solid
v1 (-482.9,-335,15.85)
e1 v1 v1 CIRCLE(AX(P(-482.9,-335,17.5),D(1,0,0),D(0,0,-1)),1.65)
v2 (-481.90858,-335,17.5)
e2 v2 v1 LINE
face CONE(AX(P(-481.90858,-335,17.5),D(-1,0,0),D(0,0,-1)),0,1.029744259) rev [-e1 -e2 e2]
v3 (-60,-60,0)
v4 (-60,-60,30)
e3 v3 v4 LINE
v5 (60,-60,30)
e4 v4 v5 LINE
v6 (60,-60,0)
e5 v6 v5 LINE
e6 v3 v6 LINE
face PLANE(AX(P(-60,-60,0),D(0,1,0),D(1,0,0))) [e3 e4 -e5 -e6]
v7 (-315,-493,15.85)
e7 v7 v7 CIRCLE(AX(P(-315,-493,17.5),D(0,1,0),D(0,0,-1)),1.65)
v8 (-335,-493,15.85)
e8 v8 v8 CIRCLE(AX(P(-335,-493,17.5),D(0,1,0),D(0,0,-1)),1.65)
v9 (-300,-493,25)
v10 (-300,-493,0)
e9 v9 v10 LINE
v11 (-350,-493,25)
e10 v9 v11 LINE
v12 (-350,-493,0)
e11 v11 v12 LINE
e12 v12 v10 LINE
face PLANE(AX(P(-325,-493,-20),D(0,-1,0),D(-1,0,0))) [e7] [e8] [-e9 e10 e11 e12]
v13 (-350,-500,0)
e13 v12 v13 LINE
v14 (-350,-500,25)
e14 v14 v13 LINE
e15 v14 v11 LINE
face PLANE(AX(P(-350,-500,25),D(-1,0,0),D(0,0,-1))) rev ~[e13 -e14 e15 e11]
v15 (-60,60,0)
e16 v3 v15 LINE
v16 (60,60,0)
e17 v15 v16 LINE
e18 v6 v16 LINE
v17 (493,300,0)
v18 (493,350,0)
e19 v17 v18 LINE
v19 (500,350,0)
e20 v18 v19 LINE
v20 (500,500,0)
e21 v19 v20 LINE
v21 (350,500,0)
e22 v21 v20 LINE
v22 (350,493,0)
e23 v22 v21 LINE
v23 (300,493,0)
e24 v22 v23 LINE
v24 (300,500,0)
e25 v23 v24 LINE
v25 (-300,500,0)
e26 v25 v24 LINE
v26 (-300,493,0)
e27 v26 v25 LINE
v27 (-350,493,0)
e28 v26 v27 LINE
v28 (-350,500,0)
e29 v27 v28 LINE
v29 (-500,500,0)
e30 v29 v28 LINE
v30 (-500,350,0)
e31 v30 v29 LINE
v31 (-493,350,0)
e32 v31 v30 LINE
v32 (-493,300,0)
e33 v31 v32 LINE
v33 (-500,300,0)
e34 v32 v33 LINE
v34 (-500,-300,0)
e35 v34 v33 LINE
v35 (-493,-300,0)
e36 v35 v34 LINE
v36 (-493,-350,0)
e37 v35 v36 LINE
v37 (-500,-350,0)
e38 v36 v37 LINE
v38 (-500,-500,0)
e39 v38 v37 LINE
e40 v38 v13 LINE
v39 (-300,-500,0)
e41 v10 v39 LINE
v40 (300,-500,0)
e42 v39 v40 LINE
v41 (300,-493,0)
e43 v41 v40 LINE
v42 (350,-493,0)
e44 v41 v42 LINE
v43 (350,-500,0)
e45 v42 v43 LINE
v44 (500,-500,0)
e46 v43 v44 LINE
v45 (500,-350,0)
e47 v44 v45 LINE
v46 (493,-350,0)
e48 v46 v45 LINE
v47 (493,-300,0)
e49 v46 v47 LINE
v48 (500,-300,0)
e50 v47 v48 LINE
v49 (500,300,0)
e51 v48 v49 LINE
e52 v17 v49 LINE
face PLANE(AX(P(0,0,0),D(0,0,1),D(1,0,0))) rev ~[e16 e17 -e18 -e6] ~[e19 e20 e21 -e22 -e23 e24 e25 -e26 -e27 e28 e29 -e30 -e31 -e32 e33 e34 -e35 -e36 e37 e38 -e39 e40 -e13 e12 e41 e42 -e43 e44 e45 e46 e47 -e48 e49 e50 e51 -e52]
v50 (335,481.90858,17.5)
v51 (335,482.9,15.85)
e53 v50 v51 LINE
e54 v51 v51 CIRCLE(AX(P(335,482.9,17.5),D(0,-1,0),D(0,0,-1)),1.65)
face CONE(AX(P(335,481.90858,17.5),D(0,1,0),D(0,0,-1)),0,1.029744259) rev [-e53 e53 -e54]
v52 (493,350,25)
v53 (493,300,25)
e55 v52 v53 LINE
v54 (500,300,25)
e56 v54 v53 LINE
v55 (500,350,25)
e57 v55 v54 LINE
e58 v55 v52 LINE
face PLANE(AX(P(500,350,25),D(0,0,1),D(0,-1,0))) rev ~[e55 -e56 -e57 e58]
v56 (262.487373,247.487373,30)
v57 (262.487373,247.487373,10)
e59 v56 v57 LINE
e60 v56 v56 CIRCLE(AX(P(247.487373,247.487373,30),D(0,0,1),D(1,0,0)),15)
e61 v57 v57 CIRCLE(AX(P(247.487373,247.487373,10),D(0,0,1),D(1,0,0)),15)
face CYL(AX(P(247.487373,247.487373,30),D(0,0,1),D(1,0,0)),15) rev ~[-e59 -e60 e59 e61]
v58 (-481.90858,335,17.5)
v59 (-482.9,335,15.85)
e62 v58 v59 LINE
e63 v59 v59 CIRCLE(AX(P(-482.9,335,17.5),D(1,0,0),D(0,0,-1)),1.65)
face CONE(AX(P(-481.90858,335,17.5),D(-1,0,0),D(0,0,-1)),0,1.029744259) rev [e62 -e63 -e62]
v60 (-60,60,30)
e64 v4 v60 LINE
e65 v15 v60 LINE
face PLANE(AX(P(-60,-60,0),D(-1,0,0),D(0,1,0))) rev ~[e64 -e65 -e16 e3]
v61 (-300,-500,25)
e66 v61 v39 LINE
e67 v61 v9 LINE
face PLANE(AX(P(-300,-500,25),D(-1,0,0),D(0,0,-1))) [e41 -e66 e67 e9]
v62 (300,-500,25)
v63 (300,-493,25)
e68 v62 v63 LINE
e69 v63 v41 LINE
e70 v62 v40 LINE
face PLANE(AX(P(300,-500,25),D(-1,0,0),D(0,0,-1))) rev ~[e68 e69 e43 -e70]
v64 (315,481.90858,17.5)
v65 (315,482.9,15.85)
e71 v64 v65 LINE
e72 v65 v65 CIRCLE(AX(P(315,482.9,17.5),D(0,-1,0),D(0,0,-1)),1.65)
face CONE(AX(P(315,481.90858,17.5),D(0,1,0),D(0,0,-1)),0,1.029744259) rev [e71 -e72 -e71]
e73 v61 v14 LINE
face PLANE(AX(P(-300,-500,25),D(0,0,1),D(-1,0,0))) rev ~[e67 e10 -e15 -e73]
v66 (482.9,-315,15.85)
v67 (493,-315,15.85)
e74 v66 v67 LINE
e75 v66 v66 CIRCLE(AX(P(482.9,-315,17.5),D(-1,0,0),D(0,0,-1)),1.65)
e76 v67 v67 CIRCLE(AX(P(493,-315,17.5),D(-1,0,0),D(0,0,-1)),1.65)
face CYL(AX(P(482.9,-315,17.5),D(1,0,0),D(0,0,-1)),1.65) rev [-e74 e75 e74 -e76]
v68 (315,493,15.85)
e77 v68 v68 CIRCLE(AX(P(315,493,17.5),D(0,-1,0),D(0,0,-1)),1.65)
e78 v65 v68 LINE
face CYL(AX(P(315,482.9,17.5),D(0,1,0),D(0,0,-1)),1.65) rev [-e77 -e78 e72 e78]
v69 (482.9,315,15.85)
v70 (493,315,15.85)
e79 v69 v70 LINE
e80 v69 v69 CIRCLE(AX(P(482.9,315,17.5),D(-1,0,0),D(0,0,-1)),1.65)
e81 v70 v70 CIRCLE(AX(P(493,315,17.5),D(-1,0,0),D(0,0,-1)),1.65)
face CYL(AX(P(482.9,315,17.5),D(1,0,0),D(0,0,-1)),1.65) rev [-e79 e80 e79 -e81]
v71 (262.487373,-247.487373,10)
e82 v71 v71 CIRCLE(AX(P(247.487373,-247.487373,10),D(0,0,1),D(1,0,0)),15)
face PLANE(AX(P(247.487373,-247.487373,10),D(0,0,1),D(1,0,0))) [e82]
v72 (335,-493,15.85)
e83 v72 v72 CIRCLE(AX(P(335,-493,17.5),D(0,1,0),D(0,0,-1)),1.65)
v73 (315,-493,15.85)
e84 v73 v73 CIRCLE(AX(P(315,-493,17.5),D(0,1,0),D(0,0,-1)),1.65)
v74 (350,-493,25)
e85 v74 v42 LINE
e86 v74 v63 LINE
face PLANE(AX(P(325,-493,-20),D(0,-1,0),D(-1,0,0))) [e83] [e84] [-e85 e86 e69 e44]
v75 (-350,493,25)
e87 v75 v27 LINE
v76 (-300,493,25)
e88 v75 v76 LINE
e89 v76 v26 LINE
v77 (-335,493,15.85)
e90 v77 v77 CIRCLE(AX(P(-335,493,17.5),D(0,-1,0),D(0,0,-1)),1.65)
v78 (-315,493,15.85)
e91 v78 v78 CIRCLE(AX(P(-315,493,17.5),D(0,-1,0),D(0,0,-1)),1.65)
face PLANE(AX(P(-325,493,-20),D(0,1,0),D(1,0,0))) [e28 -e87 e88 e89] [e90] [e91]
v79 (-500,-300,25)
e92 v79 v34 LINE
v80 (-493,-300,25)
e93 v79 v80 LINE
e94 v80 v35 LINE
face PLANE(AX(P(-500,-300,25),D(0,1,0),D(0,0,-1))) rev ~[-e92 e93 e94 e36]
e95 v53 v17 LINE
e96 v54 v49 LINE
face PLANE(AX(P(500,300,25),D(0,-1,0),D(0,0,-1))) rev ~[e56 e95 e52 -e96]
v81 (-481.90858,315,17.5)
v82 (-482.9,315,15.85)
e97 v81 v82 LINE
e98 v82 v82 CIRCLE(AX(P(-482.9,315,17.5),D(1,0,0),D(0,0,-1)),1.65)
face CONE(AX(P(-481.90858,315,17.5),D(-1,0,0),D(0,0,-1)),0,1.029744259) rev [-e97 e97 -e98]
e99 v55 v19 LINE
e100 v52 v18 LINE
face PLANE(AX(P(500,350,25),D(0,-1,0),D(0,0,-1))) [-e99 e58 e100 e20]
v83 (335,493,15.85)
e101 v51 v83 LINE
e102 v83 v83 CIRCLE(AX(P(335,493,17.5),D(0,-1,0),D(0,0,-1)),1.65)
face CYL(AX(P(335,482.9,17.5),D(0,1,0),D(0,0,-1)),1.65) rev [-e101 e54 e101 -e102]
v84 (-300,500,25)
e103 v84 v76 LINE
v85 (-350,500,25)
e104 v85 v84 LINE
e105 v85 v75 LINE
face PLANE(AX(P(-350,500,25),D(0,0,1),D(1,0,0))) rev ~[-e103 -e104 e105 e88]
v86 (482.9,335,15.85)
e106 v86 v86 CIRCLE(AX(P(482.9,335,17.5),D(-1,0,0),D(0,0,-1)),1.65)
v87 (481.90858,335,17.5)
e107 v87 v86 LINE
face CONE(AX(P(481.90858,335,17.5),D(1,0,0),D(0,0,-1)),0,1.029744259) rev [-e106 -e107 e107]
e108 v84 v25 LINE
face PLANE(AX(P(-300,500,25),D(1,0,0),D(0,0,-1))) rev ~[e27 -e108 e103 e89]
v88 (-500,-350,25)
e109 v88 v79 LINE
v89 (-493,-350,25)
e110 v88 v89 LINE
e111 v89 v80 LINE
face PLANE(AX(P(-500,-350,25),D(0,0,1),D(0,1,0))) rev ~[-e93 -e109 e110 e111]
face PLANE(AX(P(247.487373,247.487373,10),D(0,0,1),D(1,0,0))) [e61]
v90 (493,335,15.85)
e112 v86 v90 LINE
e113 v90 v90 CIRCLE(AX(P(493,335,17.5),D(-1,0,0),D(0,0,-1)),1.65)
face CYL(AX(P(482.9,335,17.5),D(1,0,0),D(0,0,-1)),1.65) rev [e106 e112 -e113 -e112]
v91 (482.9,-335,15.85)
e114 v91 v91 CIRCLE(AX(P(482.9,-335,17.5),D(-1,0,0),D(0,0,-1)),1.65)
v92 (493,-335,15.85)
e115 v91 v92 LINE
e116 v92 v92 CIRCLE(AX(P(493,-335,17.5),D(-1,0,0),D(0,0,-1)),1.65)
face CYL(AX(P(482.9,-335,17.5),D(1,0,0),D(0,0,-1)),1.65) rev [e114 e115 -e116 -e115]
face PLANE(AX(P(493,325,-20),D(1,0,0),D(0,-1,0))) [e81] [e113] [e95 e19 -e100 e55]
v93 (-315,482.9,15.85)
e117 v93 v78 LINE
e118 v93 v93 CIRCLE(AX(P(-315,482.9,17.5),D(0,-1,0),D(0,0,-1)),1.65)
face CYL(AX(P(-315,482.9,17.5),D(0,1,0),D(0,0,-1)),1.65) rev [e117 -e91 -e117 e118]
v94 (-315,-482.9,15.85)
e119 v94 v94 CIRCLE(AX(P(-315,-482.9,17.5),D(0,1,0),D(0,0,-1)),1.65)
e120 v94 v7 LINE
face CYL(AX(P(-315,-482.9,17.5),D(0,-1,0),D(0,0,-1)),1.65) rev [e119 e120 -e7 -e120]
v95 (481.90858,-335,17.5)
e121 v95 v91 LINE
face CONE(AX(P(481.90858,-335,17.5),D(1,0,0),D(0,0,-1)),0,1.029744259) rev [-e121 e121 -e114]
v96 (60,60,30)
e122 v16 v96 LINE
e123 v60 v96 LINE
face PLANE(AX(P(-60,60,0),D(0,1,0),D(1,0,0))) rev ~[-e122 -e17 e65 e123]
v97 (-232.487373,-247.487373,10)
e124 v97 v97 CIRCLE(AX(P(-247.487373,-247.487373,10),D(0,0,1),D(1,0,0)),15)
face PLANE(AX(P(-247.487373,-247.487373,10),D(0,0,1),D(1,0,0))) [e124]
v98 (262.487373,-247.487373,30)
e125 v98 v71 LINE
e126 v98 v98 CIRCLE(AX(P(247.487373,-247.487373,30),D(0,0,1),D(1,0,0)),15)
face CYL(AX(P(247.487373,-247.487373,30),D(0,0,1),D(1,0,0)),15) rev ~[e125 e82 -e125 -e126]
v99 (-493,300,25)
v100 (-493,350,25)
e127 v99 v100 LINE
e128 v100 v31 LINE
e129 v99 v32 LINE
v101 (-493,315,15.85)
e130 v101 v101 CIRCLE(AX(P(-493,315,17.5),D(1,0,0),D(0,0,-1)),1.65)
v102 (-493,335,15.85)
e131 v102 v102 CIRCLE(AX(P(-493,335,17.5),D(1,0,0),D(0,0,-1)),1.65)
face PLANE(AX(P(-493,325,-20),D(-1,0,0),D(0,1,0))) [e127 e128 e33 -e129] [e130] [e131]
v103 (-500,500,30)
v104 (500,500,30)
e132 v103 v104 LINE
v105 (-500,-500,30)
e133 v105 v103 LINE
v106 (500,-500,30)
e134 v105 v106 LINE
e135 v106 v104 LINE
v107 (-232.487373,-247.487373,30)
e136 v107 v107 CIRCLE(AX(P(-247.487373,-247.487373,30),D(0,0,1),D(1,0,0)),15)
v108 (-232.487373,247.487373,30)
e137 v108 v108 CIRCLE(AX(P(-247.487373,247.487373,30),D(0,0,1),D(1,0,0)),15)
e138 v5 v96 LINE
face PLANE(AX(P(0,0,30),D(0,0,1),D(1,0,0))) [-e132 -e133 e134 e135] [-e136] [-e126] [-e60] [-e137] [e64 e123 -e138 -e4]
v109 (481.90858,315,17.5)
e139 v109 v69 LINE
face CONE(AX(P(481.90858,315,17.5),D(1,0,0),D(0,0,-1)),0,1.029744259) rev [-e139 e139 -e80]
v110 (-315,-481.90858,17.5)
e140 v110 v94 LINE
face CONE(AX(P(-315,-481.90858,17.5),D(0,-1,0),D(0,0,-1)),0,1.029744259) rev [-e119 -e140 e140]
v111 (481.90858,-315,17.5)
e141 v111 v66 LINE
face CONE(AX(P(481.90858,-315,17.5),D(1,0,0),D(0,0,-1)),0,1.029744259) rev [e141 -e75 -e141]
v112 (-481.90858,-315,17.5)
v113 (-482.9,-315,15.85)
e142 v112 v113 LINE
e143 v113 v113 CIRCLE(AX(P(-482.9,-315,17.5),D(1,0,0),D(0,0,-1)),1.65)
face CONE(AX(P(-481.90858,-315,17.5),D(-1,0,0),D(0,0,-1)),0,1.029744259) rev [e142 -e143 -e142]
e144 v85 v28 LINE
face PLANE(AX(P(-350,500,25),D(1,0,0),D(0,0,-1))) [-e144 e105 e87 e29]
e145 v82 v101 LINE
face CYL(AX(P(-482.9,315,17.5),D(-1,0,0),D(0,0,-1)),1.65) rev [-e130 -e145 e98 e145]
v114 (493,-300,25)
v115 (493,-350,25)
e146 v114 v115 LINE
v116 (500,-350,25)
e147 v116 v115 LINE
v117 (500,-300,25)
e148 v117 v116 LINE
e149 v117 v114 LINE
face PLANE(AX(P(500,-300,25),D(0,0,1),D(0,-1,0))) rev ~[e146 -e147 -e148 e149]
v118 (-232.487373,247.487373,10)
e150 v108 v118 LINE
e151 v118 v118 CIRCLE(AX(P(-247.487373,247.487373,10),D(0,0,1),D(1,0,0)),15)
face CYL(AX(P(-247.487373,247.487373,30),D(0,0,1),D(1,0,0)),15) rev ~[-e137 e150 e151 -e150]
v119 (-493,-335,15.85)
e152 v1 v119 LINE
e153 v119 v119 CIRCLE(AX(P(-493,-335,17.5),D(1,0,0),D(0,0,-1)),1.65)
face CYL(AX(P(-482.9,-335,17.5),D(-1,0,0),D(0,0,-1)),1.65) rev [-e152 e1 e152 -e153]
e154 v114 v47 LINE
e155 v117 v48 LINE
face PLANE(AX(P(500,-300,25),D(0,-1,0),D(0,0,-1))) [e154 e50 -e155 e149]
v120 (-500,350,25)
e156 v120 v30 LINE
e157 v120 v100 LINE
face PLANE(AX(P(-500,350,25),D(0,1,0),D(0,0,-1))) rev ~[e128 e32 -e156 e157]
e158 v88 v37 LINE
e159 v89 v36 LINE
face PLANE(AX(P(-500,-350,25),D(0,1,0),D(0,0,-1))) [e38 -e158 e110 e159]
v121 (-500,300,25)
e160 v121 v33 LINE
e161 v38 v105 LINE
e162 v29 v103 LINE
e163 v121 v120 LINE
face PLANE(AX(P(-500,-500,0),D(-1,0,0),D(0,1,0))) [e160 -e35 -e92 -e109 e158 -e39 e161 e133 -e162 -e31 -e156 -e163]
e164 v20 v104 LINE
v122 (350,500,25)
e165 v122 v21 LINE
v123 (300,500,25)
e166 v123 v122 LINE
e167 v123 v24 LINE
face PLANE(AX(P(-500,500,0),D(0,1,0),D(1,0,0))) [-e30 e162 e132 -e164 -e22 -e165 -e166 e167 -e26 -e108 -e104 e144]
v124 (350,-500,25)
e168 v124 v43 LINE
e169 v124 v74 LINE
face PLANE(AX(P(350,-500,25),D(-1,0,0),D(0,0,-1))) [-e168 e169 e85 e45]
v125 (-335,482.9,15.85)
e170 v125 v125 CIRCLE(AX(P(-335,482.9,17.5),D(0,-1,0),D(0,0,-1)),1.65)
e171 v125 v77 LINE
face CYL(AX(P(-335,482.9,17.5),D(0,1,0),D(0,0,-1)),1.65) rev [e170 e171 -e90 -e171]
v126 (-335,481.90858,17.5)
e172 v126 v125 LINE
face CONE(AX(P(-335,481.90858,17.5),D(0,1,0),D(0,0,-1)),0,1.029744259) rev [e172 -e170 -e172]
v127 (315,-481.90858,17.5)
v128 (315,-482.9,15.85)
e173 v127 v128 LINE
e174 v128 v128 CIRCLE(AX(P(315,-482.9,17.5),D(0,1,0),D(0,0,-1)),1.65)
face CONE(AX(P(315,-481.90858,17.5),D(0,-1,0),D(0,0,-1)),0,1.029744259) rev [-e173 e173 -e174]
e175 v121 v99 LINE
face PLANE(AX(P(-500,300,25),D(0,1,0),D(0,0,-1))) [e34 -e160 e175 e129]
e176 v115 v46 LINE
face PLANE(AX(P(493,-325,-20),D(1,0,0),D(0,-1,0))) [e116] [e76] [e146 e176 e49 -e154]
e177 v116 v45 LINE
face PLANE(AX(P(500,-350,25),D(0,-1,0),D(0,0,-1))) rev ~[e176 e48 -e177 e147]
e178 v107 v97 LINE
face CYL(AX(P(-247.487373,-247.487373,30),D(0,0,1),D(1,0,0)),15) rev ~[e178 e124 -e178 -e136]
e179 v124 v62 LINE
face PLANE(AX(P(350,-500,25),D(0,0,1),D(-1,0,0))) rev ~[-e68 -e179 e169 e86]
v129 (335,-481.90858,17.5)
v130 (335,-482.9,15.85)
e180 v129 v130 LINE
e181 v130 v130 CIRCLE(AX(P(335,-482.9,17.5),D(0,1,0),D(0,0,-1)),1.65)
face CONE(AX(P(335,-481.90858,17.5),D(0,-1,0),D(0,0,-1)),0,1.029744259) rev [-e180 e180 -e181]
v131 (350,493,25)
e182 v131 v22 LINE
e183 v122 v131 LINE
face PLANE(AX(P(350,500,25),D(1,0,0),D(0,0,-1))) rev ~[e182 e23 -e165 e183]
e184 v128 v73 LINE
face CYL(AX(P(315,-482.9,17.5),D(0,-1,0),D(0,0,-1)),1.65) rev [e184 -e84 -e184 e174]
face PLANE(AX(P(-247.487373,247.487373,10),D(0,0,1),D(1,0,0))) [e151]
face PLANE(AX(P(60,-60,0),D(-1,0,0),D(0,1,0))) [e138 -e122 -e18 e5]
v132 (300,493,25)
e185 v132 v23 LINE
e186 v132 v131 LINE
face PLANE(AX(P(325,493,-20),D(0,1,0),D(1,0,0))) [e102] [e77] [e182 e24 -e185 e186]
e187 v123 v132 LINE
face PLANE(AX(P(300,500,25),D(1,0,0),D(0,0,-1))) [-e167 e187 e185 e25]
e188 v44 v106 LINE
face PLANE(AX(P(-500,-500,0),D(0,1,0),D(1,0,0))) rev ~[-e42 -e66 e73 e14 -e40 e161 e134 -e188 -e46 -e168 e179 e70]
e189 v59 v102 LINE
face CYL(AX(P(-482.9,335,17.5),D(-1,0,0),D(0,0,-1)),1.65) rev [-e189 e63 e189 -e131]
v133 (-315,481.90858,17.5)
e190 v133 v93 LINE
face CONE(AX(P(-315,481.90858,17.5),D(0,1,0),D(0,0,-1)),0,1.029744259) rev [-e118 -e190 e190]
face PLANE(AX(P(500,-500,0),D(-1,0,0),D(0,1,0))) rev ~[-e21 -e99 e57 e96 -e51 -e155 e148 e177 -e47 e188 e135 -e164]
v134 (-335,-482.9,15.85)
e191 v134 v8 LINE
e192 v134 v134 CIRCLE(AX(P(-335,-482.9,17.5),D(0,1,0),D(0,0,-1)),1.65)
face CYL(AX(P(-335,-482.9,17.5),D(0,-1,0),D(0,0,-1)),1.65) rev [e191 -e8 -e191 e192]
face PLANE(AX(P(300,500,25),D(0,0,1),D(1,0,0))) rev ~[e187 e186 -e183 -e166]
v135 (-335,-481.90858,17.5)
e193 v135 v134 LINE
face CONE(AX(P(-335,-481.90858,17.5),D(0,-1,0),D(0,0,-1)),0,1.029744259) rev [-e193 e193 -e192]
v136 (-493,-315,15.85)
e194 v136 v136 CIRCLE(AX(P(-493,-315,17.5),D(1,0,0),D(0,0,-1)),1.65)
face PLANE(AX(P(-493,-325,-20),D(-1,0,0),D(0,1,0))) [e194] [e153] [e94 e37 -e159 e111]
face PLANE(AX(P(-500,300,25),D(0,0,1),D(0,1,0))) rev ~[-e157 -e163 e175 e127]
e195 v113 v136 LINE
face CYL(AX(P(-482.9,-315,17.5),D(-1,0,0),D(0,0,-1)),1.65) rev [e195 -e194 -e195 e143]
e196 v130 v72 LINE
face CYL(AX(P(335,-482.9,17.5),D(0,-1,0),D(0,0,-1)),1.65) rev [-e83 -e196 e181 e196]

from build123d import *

# Parameters (mm, degrees)
SKETCH1_W                  = 1000
SKETCH1_H                  = 1000
SKETCH1_W_2                = 120
SKETCH1_H_2                = 120
BOSS_EXTRUDE1_DEPTH        = 30
SKETCH2_R                  = 15
CUT_EXTRUDE1_DEPTH         = 20
SKETCH3_W                  = 50
SKETCH3_H                  = 90
CUT_EXTRUDE2_DEPTH         = 7
CIRPATTERN1_COUNT          = 4
M4_TAPPED_HOLE1_AT_2_COUNT = 2
M4_TAPPED_HOLE1_AT_2_PITCH = 20
M4_TAPPED_HOLE1_AT_3_COUNT = 2
M4_TAPPED_HOLE1_AT_3_PITCH = 650
M4_TAPPED_HOLE1_AT_4_COUNT = 2
M4_TAPPED_HOLE1_AT_4_PITCH = 670
CIRPATTERN2_COUNT          = 4


with BuildPart() as part:
    # Sketch1 → Boss-Extrude1 (new body)
    with BuildSketch(Plane.XY):
        Rectangle(SKETCH1_W, SKETCH1_H)
        Rectangle(SKETCH1_W_2, SKETCH1_H_2, mode=Mode.SUBTRACT)
    extrude(amount=BOSS_EXTRUDE1_DEPTH)

    # Sketch2 → Cut-Extrude1 (cut)
    with BuildSketch(Plane.XY.offset(30)):
        with Locations((-247.487373415, 247.487373415)):
            Circle(SKETCH2_R)
        with Locations((247.487373415, 247.487373415)):
            Circle(SKETCH2_R)
        with Locations((247.487373415, -247.487373415)):
            Circle(SKETCH2_R)
        with Locations((-247.487373415, -247.487373415)):
            Circle(SKETCH2_R)
    extrude(amount=-CUT_EXTRUDE1_DEPTH, mode=Mode.SUBTRACT)

    # Sketch3 → Cut-Extrude2 (cut)
    with BuildSketch(Plane(origin=(0, 500, 0), x_dir=(1, 0, 0), z_dir=(0, 1, 0))):
        with Locations((-325, 20)):
            Rectangle(SKETCH3_W, SKETCH3_H)
        with Locations((325, 20)):
            Rectangle(SKETCH3_W, SKETCH3_H)
    cut_extrude2 = extrude(amount=-CUT_EXTRUDE2_DEPTH, mode=Mode.SUBTRACT)

    # CirPattern1: Cut-Extrude2 ×4 about axis
    cirpattern1_axis = Axis((0, 0, 0), (0, 0, 1))
    for i in range(1, CIRPATTERN1_COUNT):
        add(cut_extrude2.rotate(cirpattern1_axis, i * 360 / CIRPATTERN1_COUNT), mode=Mode.SUBTRACT)

    # Sketch6 → M4 Tapped Hole1 (revolve, cut)
    with BuildSketch(Plane(origin=(335, -493, 17.5), x_dir=(0, 0, -1), z_dir=(1, 0, 0))):
        Polygon((0, 0), (0, 11.091420021), (1.65, 10.1), (1.65, 0), align=None)
    m4_tapped_hole1 = revolve(axis=Axis((335, -499.35, 17.5), (0, 1, 0)), mode=Mode.SUBTRACT)

    # M4 Tapped Hole1 at 2: M4 Tapped Hole1 ×2
    with Locations(*[(-i * M4_TAPPED_HOLE1_AT_2_PITCH, 0, 0) for i in range(1, M4_TAPPED_HOLE1_AT_2_COUNT)]):
        add(m4_tapped_hole1, mode=Mode.SUBTRACT)

    # M4 Tapped Hole1 at 3: M4 Tapped Hole1 ×2
    with Locations(*[(-i * M4_TAPPED_HOLE1_AT_3_PITCH, 0, 0) for i in range(1, M4_TAPPED_HOLE1_AT_3_COUNT)]):
        add(m4_tapped_hole1, mode=Mode.SUBTRACT)

    # M4 Tapped Hole1 at 4: M4 Tapped Hole1 ×2
    with Locations(*[(-i * M4_TAPPED_HOLE1_AT_4_PITCH, 0, 0) for i in range(1, M4_TAPPED_HOLE1_AT_4_COUNT)]):
        add(m4_tapped_hole1, mode=Mode.SUBTRACT)

    # CirPattern2: M4 Tapped Hole1 ×4 about axis
    cirpattern2_axis = Axis((0, 0, 0), (0, 0, -1))
    for i in range(1, CIRPATTERN2_COUNT):
        add(m4_tapped_hole1.rotate(cirpattern2_axis, i * 360 / CIRPATTERN2_COUNT), mode=Mode.SUBTRACT)

    # CirPattern2 copy 1 sketch → CirPattern2 copy 1 (revolve, cut)
    with BuildSketch(Plane(origin=(-493, -315, 17.5), x_dir=(0, 0, -1), z_dir=(0, -1, 0))):
        Polygon((0, 0), (0, 11.091420021), (1.65, 10.1), (1.65, 0), align=None)
    revolve(axis=Axis((-499.35, -315, 17.5), (1, 0, 0)), mode=Mode.SUBTRACT)

    # CirPattern2 copy 2 sketch → CirPattern2 copy 2 (revolve, cut)
    with BuildSketch(Plane(origin=(-315, 493, 17.5), x_dir=(0, 0, -1), z_dir=(-1, 0, 0))):
        Polygon((0, 0), (0, 11.091420021), (1.65, 10.1), (1.65, 0), align=None)
    revolve(axis=Axis((-315, 499.35, 17.5), (0, -1, 0)), mode=Mode.SUBTRACT)

    # CirPattern2 copy 3 sketch → CirPattern2 copy 3 (revolve, cut)
    with BuildSketch(Plane(origin=(493, 315, 17.5), x_dir=(0, 0, -1), z_dir=(0, 1, 0))):
        Polygon((0, 0), (0, 11.091420021), (1.65, 10.1), (1.65, 0), align=None)
    revolve(axis=Axis((499.35, 315, 17.5), (-1, 0, 0)), mode=Mode.SUBTRACT)

    # CirPattern2 copy 4 sketch → CirPattern2 copy 4 (revolve, cut)
    with BuildSketch(Plane(origin=(-493, 315, 17.5), x_dir=(0, 0, -1), z_dir=(0, -1, 0))):
        Polygon((0, 0), (0, 11.091420021), (1.65, 10.1), (1.65, 0), align=None)
    revolve(axis=Axis((-499.35, 315, 17.5), (1, 0, 0)), mode=Mode.SUBTRACT)

    # CirPattern2 copy 5 sketch → CirPattern2 copy 5 (revolve, cut)
    with BuildSketch(Plane(origin=(315, 493, 17.5), x_dir=(0, 0, -1), z_dir=(-1, 0, 0))):
        Polygon((0, 0), (0, 11.091420021), (1.65, 10.1), (1.65, 0), align=None)
    revolve(axis=Axis((315, 499.35, 17.5), (0, -1, 0)), mode=Mode.SUBTRACT)

    # CirPattern2 copy 6 sketch → CirPattern2 copy 6 (revolve, cut)
    with BuildSketch(Plane(origin=(493, -315, 17.5), x_dir=(0, 0, -1), z_dir=(0, 1, 0))):
        Polygon((0, 0), (0, 11.091420021), (1.65, 10.1), (1.65, 0), align=None)
    revolve(axis=Axis((499.35, -315, 17.5), (-1, 0, 0)), mode=Mode.SUBTRACT)

    # CirPattern2 copy 7 sketch → CirPattern2 copy 7 (revolve, cut)
    with BuildSketch(Plane(origin=(-493, 335, 17.5), x_dir=(0, 0, -1), z_dir=(0, -1, 0))):
        Polygon((0, 0), (0, 11.091420021), (1.65, 10.1), (1.65, 0), align=None)
    revolve(axis=Axis((-499.35, 335, 17.5), (1, 0, 0)), mode=Mode.SUBTRACT)

    # CirPattern2 copy 8 sketch → CirPattern2 copy 8 (revolve, cut)
    with BuildSketch(Plane(origin=(335, 493, 17.5), x_dir=(0, 0, -1), z_dir=(-1, 0, 0))):
        Polygon((0, 0), (0, 11.091420021), (1.65, 10.1), (1.65, 0), align=None)
    revolve(axis=Axis((335, 499.35, 17.5), (0, -1, 0)), mode=Mode.SUBTRACT)

    # CirPattern2 copy 9 sketch → CirPattern2 copy 9 (revolve, cut)
    with BuildSketch(Plane(origin=(493, -335, 17.5), x_dir=(0, 0, -1), z_dir=(0, 1, 0))):
        Polygon((0, 0), (0, 11.091420021), (1.65, 10.1), (1.65, 0), align=None)
    revolve(axis=Axis((499.35, -335, 17.5), (-1, 0, 0)), mode=Mode.SUBTRACT)


solid = part.part
